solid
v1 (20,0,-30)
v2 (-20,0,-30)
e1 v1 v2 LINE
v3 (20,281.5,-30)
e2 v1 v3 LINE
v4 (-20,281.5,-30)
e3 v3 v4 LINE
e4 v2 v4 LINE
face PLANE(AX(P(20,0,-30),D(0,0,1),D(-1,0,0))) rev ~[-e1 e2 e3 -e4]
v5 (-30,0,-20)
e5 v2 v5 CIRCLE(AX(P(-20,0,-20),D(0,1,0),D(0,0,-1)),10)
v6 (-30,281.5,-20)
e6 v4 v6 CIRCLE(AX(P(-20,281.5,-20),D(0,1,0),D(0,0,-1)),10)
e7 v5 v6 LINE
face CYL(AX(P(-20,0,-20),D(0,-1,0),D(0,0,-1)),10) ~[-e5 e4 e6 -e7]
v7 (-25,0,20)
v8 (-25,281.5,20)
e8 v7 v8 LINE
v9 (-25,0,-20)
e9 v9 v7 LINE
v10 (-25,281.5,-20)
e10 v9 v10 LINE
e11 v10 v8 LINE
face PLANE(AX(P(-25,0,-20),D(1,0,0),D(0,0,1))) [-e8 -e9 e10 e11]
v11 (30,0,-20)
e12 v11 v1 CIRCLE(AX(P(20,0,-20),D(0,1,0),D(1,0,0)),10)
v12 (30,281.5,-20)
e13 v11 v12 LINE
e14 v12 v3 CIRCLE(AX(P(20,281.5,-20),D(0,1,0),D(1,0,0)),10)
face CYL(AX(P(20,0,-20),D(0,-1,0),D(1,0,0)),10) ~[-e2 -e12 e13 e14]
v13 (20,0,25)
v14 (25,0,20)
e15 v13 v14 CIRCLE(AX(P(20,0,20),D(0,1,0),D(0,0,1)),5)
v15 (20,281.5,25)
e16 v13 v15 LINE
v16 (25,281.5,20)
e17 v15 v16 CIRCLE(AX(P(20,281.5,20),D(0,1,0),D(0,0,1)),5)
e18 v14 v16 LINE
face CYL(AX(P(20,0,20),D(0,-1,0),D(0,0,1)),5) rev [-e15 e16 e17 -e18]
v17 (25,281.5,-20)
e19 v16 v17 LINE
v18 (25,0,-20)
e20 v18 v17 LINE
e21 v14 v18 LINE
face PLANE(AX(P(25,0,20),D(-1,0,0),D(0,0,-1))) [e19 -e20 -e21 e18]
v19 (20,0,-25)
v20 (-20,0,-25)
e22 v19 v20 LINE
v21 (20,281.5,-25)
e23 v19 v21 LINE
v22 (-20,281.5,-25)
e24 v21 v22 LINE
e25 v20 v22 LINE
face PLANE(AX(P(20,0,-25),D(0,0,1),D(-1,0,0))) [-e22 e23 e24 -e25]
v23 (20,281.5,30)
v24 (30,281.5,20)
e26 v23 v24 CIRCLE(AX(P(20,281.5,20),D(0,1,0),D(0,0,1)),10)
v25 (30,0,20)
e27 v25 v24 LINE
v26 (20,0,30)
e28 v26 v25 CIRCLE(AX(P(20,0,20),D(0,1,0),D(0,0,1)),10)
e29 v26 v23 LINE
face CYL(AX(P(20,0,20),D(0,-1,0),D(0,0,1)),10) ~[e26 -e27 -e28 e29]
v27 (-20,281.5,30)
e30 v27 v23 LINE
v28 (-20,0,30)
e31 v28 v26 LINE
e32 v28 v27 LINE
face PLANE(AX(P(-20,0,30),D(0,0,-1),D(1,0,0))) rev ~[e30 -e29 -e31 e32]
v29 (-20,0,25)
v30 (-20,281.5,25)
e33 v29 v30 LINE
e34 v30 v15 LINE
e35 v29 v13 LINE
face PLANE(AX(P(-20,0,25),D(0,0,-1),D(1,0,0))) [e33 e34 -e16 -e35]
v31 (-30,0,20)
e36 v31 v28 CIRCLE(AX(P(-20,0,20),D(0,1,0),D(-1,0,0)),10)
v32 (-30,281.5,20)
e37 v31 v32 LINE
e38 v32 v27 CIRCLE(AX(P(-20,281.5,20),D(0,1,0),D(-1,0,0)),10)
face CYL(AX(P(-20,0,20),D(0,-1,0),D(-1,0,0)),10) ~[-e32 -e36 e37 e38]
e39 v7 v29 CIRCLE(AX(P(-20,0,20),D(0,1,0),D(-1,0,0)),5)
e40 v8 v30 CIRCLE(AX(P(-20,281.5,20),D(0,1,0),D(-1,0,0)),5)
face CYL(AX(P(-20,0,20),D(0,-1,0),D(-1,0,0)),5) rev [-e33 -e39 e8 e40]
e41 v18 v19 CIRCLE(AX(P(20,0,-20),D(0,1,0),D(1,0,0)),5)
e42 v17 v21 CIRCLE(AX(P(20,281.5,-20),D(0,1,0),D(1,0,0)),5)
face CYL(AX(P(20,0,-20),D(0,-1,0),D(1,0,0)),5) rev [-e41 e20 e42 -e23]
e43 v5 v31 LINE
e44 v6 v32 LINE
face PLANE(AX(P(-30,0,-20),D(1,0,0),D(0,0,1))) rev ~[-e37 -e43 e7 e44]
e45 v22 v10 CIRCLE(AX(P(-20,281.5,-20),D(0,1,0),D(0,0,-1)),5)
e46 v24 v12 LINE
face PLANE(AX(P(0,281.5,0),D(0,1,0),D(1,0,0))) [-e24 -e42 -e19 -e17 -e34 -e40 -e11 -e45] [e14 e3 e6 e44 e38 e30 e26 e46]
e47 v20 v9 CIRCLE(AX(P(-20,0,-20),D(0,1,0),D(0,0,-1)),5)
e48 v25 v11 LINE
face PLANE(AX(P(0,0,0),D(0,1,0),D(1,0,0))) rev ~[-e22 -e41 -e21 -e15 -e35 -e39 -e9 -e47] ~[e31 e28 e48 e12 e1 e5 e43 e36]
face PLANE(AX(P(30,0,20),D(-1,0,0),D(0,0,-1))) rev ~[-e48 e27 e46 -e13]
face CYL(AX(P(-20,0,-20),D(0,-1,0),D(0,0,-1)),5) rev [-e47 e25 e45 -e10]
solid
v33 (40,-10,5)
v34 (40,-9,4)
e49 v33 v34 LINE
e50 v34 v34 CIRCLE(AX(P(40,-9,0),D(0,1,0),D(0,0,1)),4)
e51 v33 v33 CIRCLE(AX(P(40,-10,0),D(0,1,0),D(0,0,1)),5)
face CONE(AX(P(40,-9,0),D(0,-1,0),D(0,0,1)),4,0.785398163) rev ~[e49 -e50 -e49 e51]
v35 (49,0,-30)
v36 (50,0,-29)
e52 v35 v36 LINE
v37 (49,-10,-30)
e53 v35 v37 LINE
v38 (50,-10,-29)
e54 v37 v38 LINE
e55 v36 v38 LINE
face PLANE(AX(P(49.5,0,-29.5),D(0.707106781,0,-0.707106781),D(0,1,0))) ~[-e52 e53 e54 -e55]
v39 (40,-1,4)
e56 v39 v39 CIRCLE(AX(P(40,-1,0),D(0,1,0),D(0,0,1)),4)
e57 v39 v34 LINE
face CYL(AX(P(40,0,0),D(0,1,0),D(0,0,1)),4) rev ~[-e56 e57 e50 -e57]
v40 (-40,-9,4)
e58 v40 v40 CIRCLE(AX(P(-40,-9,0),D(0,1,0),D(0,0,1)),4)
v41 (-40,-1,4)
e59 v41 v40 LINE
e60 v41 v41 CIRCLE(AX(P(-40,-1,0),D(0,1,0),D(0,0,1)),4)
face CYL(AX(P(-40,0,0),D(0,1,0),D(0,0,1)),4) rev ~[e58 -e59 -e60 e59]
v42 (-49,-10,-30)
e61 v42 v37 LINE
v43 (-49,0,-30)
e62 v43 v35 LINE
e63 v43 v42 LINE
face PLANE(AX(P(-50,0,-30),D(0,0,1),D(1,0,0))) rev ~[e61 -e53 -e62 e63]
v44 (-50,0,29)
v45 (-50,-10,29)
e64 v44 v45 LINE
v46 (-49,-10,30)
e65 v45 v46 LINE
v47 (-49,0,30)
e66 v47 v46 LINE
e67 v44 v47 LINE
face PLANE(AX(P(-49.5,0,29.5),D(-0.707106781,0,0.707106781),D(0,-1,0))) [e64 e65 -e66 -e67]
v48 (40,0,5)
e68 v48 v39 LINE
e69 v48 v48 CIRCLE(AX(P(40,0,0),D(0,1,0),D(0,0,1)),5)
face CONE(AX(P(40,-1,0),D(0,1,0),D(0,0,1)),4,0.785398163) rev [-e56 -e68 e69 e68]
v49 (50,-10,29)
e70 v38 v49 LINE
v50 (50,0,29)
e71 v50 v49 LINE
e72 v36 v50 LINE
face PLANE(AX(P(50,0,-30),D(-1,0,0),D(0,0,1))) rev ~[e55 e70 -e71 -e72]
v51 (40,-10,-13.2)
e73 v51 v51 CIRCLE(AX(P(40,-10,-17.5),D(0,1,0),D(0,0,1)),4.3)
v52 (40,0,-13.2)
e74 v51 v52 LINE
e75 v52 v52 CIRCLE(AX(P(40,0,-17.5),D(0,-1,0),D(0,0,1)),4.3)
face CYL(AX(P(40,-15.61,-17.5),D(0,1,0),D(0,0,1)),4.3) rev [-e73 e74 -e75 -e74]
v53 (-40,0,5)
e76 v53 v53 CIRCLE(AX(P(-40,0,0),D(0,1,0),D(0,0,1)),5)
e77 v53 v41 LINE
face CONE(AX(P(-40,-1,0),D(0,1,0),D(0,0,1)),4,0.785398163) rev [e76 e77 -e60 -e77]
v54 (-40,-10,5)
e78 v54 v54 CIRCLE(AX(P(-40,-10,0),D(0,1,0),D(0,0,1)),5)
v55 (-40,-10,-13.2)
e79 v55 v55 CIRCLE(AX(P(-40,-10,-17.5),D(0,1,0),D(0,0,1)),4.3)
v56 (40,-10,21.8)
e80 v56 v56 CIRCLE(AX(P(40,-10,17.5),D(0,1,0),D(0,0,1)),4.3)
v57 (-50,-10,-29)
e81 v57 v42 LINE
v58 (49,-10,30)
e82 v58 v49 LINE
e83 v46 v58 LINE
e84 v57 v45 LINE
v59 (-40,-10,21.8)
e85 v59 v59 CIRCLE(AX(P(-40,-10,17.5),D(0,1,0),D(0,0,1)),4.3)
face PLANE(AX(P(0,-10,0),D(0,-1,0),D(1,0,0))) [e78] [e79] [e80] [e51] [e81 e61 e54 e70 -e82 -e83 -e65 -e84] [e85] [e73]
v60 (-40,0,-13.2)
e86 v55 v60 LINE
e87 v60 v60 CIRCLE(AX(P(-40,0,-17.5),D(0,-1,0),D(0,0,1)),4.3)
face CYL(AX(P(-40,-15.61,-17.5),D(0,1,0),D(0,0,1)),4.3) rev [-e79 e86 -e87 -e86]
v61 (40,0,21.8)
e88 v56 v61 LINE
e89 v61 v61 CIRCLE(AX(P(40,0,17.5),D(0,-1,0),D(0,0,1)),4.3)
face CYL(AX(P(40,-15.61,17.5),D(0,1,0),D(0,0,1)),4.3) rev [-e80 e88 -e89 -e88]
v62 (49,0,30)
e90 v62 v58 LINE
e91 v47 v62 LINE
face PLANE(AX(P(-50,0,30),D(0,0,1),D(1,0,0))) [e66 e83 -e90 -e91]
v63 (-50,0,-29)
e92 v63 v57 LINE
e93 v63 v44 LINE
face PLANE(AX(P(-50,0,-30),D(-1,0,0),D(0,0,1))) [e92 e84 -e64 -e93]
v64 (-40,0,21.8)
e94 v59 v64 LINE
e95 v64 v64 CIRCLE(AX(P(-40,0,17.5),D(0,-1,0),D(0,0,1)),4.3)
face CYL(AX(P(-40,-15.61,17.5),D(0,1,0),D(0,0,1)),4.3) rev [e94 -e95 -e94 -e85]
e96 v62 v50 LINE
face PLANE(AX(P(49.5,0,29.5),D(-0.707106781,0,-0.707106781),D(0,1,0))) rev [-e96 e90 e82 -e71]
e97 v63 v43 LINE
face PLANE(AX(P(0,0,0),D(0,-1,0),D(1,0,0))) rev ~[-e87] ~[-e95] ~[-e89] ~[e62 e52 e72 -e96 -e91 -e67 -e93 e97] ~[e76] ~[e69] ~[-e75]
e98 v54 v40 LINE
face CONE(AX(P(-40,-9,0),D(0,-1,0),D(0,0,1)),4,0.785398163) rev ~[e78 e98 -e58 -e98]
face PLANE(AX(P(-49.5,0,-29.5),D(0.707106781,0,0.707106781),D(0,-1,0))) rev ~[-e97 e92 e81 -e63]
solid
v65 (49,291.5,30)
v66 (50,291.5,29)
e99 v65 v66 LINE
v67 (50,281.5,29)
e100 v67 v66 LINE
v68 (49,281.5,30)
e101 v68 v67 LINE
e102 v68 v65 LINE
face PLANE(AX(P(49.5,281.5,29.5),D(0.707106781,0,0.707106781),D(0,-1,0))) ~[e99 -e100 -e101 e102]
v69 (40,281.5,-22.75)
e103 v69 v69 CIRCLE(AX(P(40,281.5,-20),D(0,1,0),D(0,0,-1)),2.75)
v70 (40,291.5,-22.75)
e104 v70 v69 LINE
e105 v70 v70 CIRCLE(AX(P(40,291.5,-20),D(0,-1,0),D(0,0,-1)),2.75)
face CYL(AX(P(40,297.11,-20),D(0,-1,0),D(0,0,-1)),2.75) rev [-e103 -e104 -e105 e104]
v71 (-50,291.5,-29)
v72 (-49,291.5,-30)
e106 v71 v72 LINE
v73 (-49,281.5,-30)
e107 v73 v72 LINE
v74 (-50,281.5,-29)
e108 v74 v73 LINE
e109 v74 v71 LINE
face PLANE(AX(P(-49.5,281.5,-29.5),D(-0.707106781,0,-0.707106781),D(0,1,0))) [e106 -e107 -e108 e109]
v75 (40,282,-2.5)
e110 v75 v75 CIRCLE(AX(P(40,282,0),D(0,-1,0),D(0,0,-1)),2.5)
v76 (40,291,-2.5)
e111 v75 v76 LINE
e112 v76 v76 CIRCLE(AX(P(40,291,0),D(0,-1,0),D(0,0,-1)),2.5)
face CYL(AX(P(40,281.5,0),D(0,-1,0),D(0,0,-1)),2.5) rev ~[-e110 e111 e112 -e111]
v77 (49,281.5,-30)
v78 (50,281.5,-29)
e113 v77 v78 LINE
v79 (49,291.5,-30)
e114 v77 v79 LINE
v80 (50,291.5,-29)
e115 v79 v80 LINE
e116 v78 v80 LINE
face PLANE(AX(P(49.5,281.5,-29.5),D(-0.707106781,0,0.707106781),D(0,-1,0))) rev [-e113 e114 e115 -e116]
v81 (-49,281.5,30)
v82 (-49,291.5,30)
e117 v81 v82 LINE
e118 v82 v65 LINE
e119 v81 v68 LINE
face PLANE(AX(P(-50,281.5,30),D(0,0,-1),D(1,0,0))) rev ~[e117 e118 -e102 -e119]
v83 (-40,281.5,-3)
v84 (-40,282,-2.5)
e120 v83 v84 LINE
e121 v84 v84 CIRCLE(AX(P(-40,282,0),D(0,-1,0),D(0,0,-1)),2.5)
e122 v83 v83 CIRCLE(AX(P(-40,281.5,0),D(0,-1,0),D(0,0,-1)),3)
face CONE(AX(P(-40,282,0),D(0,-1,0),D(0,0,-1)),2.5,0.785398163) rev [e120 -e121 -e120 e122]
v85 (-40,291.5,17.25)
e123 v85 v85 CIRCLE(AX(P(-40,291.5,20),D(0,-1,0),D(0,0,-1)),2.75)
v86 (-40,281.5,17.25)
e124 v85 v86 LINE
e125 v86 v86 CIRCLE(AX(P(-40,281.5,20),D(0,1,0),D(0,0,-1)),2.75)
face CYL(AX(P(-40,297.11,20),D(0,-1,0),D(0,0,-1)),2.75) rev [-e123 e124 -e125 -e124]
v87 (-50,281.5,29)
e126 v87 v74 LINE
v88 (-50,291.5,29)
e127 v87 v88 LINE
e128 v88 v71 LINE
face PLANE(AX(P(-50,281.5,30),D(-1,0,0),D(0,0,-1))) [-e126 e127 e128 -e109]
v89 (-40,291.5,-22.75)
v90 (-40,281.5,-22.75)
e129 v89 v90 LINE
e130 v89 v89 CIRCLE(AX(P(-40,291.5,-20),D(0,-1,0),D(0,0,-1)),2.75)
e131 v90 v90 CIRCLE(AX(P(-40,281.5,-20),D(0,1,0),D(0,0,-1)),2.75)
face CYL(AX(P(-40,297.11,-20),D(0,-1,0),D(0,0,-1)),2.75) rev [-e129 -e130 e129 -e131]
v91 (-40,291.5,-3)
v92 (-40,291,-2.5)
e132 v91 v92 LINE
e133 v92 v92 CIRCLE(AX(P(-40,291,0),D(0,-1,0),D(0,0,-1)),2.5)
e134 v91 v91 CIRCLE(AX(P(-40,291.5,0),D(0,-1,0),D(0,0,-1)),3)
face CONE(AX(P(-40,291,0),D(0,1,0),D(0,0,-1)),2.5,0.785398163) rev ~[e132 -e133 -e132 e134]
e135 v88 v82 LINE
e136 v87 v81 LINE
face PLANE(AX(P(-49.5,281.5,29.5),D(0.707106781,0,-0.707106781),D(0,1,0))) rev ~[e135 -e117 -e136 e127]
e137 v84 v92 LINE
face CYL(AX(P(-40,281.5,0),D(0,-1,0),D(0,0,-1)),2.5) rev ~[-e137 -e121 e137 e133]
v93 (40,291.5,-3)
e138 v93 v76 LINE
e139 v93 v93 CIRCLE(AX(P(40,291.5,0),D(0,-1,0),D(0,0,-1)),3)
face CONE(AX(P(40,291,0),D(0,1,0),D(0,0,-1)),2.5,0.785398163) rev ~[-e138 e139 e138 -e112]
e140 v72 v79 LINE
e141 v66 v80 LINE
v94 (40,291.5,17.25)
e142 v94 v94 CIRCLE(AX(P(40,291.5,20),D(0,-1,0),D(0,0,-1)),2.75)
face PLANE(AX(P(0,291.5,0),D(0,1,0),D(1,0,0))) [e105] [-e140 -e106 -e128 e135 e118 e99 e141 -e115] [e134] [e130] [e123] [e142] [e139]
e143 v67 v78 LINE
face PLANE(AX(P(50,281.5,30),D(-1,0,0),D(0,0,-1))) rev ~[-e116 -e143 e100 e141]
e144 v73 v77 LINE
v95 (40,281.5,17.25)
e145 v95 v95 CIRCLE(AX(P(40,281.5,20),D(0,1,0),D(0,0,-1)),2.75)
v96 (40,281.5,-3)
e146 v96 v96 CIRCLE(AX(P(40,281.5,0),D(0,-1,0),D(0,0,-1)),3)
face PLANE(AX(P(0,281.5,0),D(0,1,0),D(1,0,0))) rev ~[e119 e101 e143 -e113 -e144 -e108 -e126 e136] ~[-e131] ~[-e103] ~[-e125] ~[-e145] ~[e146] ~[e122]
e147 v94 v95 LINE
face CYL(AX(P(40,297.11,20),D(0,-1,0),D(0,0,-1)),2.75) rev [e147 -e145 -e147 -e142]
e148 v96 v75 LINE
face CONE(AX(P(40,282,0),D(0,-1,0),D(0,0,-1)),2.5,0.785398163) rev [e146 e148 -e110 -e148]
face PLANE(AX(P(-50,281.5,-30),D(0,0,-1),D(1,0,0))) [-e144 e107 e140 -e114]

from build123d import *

# Parameters (mm, degrees)
MEMBER_1_DEPTH                   = 281.5
SKETCH_2_W                       = 100
SKETCH_2_H                       = 60
EXTRUDE_1_DEPTH                  = 10
SKETCH_3_W                       = 100
SKETCH_3_H                       = 60
EXTRUDE_2_DEPTH                  = 10
HOLE_WIZARD_8_6_8_6_1_AT_2_COUNT = 2
HOLE_WIZARD_8_6_8_6_1_AT_2_PITCH = 35
HOLE_WIZARD_8_6_8_6_1_AT_3_COUNT = 2
HOLE_WIZARD_8_6_8_6_1_AT_3_PITCH = 80
HOLE_WIZARD_8_6_8_6_1_AT_4_COUNT = 2
HOLE_WIZARD_8_6_8_6_1_AT_4_PITCH = 87.321245983
SKETCH_6_R                       = 4
CUT_EXTRUDE_1_DEPTH              = 298.274704608
CHAMFER_3_SIZE                   = 1
HOLE_WIZARD_5_5_5_5_1_AT_2_COUNT = 2
HOLE_WIZARD_5_5_5_5_1_AT_2_PITCH = 40
HOLE_WIZARD_5_5_5_5_1_AT_3_COUNT = 2
HOLE_WIZARD_5_5_5_5_1_AT_3_PITCH = 80
HOLE_WIZARD_5_5_5_5_1_AT_4_COUNT = 2
HOLE_WIZARD_5_5_5_5_1_AT_4_PITCH = 89.4427191
SKETCH_9_R                       = 2.5
CUT_EXTRUDE_2_DEPTH              = 298.274704608
CHAMFER_4_SIZE                   = 0.5
CHAMFER_5_SIZE                   = 1
CHAMFER_6_SIZE                   = 1


with BuildPart() as part:
    # Sketch11 → Member 1 (new body)
    with BuildSketch(Plane(origin=(0, 0, 0), x_dir=(1, 0, 0), z_dir=(0, 1, 0))):
        with BuildLine():
            Line((-20, -30), (20, -30))
            ThreePointArc((20, -30), (27.071067812, -27.071067812), (30, -20))
            Line((30, -20), (30, 20))
            ThreePointArc((30, 20), (27.071067812, 27.071067812), (20, 30))
            Line((20, 30), (-20, 30))
            ThreePointArc((-20, 30), (-27.071067812, 27.071067812), (-30, 20))
            Line((-30, 20), (-30, -20))
            ThreePointArc((-30, -20), (-27.071067812, -27.071067812), (-20, -30))
        make_face()
        with BuildLine():
            Line((-20, -25), (20, -25))
            ThreePointArc((20, -25), (23.535533906, -23.535533906), (25, -20))
            Line((25, -20), (25, 20))
            ThreePointArc((25, 20), (23.535533906, 23.535533906), (20, 25))
            Line((20, 25), (-20, 25))
            ThreePointArc((-20, 25), (-23.535533906, 23.535533906), (-25, 20))
            Line((-25, 20), (-25, -20))
            ThreePointArc((-25, -20), (-23.535533906, -23.535533906), (-20, -25))
        make_face(mode=Mode.SUBTRACT)
    extrude(amount=MEMBER_1_DEPTH)


with BuildPart() as body_2:
    # 草图2 → 凸台-拉伸1 (new body)
    with BuildSketch(Plane(origin=(0, 281.5, 0), x_dir=(1, 0, 0), z_dir=(0, 1, 0))):
        Rectangle(SKETCH_2_W, SKETCH_2_H)
    extrude(amount=EXTRUDE_1_DEPTH)

    # 草图7 → Ø5.5 (5.5) 直径孔1 (revolve, cut)
    with BuildSketch(Plane(origin=(-40, 281.5, -20), x_dir=(0, 0, -1), z_dir=(1, 0, 0))):
        Polygon((0, 0), (0, 17.19771324), (2.75, 15.61), (2.75, 0), align=None)
    hole_wizard_5_5_5_5_1 = revolve(axis=Axis((-40, 275.15, -20), (0, 1, 0)), mode=Mode.SUBTRACT)

    # Ø5.5 (5.5) 直径孔1 at 2: Ø5.5 (5.5) 直径孔1 ×2
    with Locations(*[(0, 0, i * HOLE_WIZARD_5_5_5_5_1_AT_2_PITCH) for i in range(1, HOLE_WIZARD_5_5_5_5_1_AT_2_COUNT)]):
        add(hole_wizard_5_5_5_5_1, mode=Mode.SUBTRACT)

    # Ø5.5 (5.5) 直径孔1 at 3: Ø5.5 (5.5) 直径孔1 ×2
    with Locations(*[(i * HOLE_WIZARD_5_5_5_5_1_AT_3_PITCH, 0, 0) for i in range(1, HOLE_WIZARD_5_5_5_5_1_AT_3_COUNT)]):
        add(hole_wizard_5_5_5_5_1, mode=Mode.SUBTRACT)

    # Ø5.5 (5.5) 直径孔1 at 4: Ø5.5 (5.5) 直径孔1 ×2
    with Locations(*[Vector(0.894427190999916, 0, 0.447213595499958) * (i * HOLE_WIZARD_5_5_5_5_1_AT_4_PITCH) for i in range(1, HOLE_WIZARD_5_5_5_5_1_AT_4_COUNT)]):
        add(hole_wizard_5_5_5_5_1, mode=Mode.SUBTRACT)

    # 草图9 → 切除-拉伸2 (cut, through all)
    with BuildSketch(Plane.XZ.offset(-281.5)):
        with Locations(Location((40, 0, 0), (0, 0, 270))):
            Circle(SKETCH_9_R)
        with Locations(Location((-40, 0, 0), (0, 0, 270))):
            Circle(SKETCH_9_R)
    extrude(amount=-CUT_EXTRUDE_2_DEPTH, mode=Mode.SUBTRACT)

    # 倒角4
    chamfer_4_edges = [body_2.edges().sort_by_distance(p)[0] for p in [
        (40, 291.5, 2.5),
        (40, 281.5, 2.5),
        (-40, 291.5, 2.5),
        (-40, 281.5, 2.5),
    ]]
    chamfer(chamfer_4_edges, length=CHAMFER_4_SIZE)

    # 倒角6
    chamfer_6_edges = [body_2.edges().sort_by_distance(p)[0] for p in [
        (50, 286.5, 30),
        (-50, 286.5, 30),
        (-50, 286.5, -30),
        (50, 286.5, -30),
    ]]
    chamfer(chamfer_6_edges, length=CHAMFER_6_SIZE)


with BuildPart() as body_3:
    # 草图3 → 凸台-拉伸2 (new body)
    with BuildSketch(Plane.XZ):
        Rectangle(SKETCH_3_W, SKETCH_3_H)
    extrude(amount=EXTRUDE_2_DEPTH)

    # 草图4 → Ø8.6 (8.6) 直径孔1 (revolve, cut)
    with BuildSketch(Plane(origin=(40, 0, -17.5), x_dir=(0, 0, 1), z_dir=(1, 0, 0))):
        Polygon((0, 0), (0, 18.092606158), (4.3, 15.61), (4.3, 0), align=None)
    hole_wizard_8_6_8_6_1 = revolve(axis=Axis((40, 6.35, -17.5), (0, -1, 0)), mode=Mode.SUBTRACT)

    # Ø8.6 (8.6) 直径孔1 at 2: Ø8.6 (8.6) 直径孔1 ×2
    with Locations(*[(0, 0, i * HOLE_WIZARD_8_6_8_6_1_AT_2_PITCH) for i in range(1, HOLE_WIZARD_8_6_8_6_1_AT_2_COUNT)]):
        add(hole_wizard_8_6_8_6_1, mode=Mode.SUBTRACT)

    # Ø8.6 (8.6) 直径孔1 at 3: Ø8.6 (8.6) 直径孔1 ×2
    with Locations(*[(-i * HOLE_WIZARD_8_6_8_6_1_AT_3_PITCH, 0, 0) for i in range(1, HOLE_WIZARD_8_6_8_6_1_AT_3_COUNT)]):
        add(hole_wizard_8_6_8_6_1, mode=Mode.SUBTRACT)

    # Ø8.6 (8.6) 直径孔1 at 4: Ø8.6 (8.6) 直径孔1 ×2
    with Locations(*[Vector(-0.9161573349021891, 0, 0.4008188340197079) * (i * HOLE_WIZARD_8_6_8_6_1_AT_4_PITCH) for i in range(1, HOLE_WIZARD_8_6_8_6_1_AT_4_COUNT)]):
        add(hole_wizard_8_6_8_6_1, mode=Mode.SUBTRACT)

    # 草图6 → 切除-拉伸1 (cut, through all)
    with BuildSketch(Plane(origin=(0, 0, 0), x_dir=(1, 0, 0), z_dir=(0, 1, 0))):
        with Locations(Location((-40, 0, 0), (0, 0, 270))):
            Circle(SKETCH_6_R)
        with Locations(Location((40, 0, 0), (0, 0, 270))):
            Circle(SKETCH_6_R)
    extrude(amount=-CUT_EXTRUDE_1_DEPTH, mode=Mode.SUBTRACT)

    # 倒角3
    chamfer_3_edges = [body_3.edges().sort_by_distance(p)[0] for p in [
        (-40, -10, -4),
        (-40, 0, -4),
        (40, -10, -4),
        (40, 0, -4),
    ]]
    chamfer(chamfer_3_edges, length=CHAMFER_3_SIZE)

    # 倒角5
    chamfer_5_edges = [body_3.edges().sort_by_distance(p)[0] for p in [
        (50, -5, -30),
        (-50, -5, -30),
        (-50, -5, 30),
        (50, -5, 30),
    ]]
    chamfer(chamfer_5_edges, length=CHAMFER_5_SIZE)


solid = Compound([part.part, body_2.part, body_3.part])
